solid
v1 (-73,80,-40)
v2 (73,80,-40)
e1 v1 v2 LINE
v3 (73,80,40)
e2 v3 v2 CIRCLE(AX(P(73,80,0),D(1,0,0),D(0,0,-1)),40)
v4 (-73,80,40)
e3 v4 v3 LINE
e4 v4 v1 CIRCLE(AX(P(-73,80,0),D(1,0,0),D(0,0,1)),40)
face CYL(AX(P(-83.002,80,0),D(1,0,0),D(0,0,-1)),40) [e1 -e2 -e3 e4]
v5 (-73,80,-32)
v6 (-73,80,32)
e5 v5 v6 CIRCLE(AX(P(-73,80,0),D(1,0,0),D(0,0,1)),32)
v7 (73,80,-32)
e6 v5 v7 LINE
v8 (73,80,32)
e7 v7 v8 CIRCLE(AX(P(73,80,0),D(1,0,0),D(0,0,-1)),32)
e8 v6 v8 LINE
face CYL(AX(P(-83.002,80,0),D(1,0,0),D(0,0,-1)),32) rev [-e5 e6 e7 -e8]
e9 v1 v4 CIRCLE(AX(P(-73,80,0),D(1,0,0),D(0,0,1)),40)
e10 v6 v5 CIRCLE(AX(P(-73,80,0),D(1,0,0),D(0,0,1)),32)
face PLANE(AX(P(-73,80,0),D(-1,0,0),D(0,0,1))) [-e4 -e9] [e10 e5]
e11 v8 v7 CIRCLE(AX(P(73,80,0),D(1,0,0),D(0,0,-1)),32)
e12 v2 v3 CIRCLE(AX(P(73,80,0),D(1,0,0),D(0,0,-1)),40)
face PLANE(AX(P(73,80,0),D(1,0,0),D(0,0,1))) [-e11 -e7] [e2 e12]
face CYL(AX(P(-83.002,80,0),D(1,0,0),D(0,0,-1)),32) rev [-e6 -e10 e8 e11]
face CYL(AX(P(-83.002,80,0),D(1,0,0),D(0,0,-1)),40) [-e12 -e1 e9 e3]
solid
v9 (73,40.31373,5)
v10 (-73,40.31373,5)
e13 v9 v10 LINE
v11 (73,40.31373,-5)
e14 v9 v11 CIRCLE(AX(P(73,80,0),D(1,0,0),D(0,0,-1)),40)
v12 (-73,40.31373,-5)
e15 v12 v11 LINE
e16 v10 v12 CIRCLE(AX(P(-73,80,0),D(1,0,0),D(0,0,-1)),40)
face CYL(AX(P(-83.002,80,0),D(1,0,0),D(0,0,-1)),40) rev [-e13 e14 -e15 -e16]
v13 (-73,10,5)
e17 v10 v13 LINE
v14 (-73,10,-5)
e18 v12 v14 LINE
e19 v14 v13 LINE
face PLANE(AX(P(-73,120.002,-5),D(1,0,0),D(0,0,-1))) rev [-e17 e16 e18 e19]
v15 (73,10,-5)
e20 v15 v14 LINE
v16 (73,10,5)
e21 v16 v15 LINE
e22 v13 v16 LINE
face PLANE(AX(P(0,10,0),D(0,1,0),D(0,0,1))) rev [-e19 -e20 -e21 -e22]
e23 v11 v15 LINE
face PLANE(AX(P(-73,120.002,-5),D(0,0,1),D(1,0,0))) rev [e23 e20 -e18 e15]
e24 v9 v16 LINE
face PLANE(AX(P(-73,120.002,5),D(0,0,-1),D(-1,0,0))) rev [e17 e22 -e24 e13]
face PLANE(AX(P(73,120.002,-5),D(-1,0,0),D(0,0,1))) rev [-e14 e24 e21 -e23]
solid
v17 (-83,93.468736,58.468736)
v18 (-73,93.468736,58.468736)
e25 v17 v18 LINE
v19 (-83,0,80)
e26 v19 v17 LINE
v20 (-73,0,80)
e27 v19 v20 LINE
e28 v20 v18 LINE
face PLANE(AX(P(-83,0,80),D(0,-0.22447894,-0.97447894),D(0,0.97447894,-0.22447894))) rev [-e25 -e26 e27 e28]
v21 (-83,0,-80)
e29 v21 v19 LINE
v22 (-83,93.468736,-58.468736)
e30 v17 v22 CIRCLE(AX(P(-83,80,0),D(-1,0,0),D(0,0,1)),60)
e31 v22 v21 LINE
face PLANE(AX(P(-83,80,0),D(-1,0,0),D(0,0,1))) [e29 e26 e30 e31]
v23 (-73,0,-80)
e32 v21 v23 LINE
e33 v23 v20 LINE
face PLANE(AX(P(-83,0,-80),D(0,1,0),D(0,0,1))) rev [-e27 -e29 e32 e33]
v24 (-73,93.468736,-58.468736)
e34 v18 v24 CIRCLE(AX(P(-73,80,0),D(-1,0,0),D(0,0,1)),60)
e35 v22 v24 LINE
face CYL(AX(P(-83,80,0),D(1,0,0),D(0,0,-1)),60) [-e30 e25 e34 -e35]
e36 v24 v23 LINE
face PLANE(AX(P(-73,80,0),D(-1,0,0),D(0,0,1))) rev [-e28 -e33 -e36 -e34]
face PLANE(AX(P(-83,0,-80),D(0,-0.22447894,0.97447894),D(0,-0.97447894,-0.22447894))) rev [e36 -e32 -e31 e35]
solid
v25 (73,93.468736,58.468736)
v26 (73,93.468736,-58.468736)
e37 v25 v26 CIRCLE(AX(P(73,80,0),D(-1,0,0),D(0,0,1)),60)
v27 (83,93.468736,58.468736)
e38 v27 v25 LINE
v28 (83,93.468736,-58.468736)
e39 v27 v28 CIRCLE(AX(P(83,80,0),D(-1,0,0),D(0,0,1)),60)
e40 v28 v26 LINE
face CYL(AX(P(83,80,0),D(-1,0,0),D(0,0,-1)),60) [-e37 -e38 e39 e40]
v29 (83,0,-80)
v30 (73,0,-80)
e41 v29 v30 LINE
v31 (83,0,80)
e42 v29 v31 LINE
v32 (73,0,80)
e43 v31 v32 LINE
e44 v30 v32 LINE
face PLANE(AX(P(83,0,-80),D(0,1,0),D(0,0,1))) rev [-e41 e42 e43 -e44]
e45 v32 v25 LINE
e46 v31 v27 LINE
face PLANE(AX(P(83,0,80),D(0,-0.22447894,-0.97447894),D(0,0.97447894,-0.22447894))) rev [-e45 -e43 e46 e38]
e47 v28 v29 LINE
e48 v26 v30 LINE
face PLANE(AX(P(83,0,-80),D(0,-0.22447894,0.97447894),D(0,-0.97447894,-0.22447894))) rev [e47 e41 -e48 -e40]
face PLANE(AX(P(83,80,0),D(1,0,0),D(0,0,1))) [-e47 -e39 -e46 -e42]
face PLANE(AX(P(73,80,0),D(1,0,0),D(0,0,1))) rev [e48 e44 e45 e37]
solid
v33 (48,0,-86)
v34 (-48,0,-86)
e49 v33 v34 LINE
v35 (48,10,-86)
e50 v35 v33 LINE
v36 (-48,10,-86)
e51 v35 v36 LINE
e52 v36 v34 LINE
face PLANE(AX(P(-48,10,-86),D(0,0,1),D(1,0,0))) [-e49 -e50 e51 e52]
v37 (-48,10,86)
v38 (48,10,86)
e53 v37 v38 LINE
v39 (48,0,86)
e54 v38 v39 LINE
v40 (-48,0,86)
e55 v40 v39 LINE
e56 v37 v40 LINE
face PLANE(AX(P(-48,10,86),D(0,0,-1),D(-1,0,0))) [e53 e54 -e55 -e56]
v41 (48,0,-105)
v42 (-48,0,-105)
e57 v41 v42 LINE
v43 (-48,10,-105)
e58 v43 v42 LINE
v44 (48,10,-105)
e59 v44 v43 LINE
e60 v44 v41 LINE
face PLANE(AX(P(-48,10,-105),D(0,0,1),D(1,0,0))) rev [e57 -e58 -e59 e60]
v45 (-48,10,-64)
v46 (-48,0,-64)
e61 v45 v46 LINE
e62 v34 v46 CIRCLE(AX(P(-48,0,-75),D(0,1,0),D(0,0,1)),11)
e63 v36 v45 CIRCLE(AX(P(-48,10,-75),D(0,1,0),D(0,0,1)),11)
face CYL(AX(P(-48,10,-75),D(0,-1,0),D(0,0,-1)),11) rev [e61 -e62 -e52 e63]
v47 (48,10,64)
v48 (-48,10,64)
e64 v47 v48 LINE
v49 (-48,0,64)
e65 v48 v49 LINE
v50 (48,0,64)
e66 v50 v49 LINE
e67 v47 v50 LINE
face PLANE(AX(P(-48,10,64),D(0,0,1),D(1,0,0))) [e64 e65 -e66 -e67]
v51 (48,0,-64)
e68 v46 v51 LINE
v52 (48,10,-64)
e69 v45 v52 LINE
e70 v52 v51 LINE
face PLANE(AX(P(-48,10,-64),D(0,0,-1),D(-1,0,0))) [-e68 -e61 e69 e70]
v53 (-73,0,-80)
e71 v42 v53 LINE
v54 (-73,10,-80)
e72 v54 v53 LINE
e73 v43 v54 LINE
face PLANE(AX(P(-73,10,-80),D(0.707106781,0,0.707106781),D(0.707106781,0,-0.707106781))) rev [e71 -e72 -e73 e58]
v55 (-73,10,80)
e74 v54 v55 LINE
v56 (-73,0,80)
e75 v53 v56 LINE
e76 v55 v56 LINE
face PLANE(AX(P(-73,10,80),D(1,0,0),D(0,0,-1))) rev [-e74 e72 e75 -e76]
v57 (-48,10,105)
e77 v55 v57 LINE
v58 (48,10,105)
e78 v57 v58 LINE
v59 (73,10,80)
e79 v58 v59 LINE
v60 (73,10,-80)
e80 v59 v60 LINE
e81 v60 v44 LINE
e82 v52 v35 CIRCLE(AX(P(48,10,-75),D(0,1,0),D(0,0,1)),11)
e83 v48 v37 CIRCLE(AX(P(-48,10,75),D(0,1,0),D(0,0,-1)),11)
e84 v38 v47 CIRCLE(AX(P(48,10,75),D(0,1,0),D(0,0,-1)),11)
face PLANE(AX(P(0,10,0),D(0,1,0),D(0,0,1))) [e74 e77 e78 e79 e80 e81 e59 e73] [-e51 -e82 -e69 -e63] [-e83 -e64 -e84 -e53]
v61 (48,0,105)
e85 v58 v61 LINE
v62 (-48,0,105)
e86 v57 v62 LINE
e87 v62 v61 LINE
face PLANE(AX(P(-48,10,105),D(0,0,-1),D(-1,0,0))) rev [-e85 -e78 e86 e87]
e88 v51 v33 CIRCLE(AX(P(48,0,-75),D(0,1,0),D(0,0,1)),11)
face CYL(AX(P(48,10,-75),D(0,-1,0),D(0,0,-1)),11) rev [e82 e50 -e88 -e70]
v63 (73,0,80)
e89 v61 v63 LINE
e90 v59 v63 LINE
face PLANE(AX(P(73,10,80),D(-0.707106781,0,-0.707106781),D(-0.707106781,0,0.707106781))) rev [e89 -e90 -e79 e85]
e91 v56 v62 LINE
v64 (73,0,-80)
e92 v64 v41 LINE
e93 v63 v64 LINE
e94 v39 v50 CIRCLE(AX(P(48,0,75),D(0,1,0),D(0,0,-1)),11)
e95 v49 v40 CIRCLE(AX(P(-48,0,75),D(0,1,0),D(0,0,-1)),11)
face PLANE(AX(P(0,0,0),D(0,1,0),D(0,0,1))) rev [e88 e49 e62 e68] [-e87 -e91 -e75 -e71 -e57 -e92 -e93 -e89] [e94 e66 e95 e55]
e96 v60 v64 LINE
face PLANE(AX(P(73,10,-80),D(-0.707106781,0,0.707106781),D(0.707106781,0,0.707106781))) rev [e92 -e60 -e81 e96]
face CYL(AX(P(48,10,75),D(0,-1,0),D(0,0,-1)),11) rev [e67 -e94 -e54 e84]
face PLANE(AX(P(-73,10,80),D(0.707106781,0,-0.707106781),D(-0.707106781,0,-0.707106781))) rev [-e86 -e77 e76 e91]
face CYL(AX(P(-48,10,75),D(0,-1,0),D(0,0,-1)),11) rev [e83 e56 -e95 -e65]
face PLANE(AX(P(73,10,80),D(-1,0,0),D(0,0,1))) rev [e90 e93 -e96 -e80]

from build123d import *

# Parameters (mm, degrees)
EXTRUDE_1_DEPTH      = 10
EXTRUDE_2_DEPTH      = 10
EXTRUDE_3_DEPTH      = 73
EXTRUDE_3_DEPTH_BACK = 73
SKETCH_3_R           = 40
SKETCH_3_R_2         = 32
EXTRUDE_4_REACH      = 188.585
EXTRUDE_4_END_RADIUS = 40
SKETCH_4_W           = 146
SKETCH_4_H           = 10


with BuildPart() as part:
    # 草图1 → 凸台-拉伸1 (new body)
    with BuildSketch(Plane(origin=(0, 0, 0), x_dir=(1, 0, 0), z_dir=(0, 1, 0))):
        Polygon((-73, -80), (-73, 80), (-48, 105), (48, 105), (73, 80), (73, -80), (48, -105), (-48, -105), align=None)
        with BuildLine():
            Line((-48, 86), (48, 86))
            ThreePointArc((48, 86), (59, 75), (48, 64))
            Line((48, 64), (-48, 64))
            ThreePointArc((-48, 64), (-59, 75), (-48, 86))
        make_face(mode=Mode.SUBTRACT)
        with BuildLine():
            Line((-48, -86), (48, -86))
            ThreePointArc((48, -86), (59, -75), (48, -64))
            Line((48, -64), (-48, -64))
            ThreePointArc((-48, -64), (-59, -75), (-48, -86))
        make_face(mode=Mode.SUBTRACT)
    extrude(amount=EXTRUDE_1_DEPTH)


with BuildPart() as body_2:
    # 草图2 → 凸台-拉伸2 (new body)
    with BuildSketch(Plane.ZY.offset(73)):
        with BuildLine():
            Line((-80, 0), (-58.468736425, 93.468736425))
            ThreePointArc((-58.468736425, 93.468736425), (0, 140), (58.468736425, 93.468736425))
            Line((58.468736425, 93.468736425), (80, 0))
            Line((80, 0), (-80, 0))
        make_face()
    extrude(amount=EXTRUDE_2_DEPTH)


with BuildPart() as body_3:
    # 镜向1: mirrored copy
    add(body_2.part.mirror(Plane(origin=(0, 0, 0), x_dir=(0, 0, 1), z_dir=(1, 0, 0))))


with BuildPart() as body_4:
    # 草图3 → 凸台-拉伸3 (new, two sides: drawn at the far end of the back side and taken through both)
    with BuildSketch(Plane(origin=(0, 0, 0), x_dir=(0, 0, -1), z_dir=(1, 0, 0)).offset(-EXTRUDE_3_DEPTH_BACK)):
        with Locations((0, 80)):
            Circle(SKETCH_3_R)
        with Locations((0, 80)):
            Circle(SKETCH_3_R_2, mode=Mode.SUBTRACT)
    extrude(amount=EXTRUDE_3_DEPTH + EXTRUDE_3_DEPTH_BACK)


with BuildPart() as body_5:
    # 凸台-拉伸4: up to this cylinder (the profile starts outside it)
    extrude_4_end = Plane(origin=(0, 80, 0), z_dir=(1, 0, 0)) * Cylinder(EXTRUDE_4_END_RADIUS, 458.17, mode=Mode.PRIVATE)
    # 草图4 → 凸台-拉伸4 (new, up to the surface)
    with BuildSketch(Plane(origin=(0, 10, 0), x_dir=(1, 0, 0), z_dir=(0, 1, 0)), mode=Mode.PRIVATE) as extrude_4_sk1:
        Rectangle(SKETCH_4_W, SKETCH_4_H)
    extrude_4_tool1 = extrude(extrude_4_sk1.sketch, amount=EXTRUDE_4_REACH, mode=Mode.PRIVATE) - extrude_4_end
    add(extrude_4_tool1.solids().sort_by_distance((0, 10, 0))[0])


solid = Compound([part.part, body_2.part, body_3.part, body_4.part, body_5.part])
